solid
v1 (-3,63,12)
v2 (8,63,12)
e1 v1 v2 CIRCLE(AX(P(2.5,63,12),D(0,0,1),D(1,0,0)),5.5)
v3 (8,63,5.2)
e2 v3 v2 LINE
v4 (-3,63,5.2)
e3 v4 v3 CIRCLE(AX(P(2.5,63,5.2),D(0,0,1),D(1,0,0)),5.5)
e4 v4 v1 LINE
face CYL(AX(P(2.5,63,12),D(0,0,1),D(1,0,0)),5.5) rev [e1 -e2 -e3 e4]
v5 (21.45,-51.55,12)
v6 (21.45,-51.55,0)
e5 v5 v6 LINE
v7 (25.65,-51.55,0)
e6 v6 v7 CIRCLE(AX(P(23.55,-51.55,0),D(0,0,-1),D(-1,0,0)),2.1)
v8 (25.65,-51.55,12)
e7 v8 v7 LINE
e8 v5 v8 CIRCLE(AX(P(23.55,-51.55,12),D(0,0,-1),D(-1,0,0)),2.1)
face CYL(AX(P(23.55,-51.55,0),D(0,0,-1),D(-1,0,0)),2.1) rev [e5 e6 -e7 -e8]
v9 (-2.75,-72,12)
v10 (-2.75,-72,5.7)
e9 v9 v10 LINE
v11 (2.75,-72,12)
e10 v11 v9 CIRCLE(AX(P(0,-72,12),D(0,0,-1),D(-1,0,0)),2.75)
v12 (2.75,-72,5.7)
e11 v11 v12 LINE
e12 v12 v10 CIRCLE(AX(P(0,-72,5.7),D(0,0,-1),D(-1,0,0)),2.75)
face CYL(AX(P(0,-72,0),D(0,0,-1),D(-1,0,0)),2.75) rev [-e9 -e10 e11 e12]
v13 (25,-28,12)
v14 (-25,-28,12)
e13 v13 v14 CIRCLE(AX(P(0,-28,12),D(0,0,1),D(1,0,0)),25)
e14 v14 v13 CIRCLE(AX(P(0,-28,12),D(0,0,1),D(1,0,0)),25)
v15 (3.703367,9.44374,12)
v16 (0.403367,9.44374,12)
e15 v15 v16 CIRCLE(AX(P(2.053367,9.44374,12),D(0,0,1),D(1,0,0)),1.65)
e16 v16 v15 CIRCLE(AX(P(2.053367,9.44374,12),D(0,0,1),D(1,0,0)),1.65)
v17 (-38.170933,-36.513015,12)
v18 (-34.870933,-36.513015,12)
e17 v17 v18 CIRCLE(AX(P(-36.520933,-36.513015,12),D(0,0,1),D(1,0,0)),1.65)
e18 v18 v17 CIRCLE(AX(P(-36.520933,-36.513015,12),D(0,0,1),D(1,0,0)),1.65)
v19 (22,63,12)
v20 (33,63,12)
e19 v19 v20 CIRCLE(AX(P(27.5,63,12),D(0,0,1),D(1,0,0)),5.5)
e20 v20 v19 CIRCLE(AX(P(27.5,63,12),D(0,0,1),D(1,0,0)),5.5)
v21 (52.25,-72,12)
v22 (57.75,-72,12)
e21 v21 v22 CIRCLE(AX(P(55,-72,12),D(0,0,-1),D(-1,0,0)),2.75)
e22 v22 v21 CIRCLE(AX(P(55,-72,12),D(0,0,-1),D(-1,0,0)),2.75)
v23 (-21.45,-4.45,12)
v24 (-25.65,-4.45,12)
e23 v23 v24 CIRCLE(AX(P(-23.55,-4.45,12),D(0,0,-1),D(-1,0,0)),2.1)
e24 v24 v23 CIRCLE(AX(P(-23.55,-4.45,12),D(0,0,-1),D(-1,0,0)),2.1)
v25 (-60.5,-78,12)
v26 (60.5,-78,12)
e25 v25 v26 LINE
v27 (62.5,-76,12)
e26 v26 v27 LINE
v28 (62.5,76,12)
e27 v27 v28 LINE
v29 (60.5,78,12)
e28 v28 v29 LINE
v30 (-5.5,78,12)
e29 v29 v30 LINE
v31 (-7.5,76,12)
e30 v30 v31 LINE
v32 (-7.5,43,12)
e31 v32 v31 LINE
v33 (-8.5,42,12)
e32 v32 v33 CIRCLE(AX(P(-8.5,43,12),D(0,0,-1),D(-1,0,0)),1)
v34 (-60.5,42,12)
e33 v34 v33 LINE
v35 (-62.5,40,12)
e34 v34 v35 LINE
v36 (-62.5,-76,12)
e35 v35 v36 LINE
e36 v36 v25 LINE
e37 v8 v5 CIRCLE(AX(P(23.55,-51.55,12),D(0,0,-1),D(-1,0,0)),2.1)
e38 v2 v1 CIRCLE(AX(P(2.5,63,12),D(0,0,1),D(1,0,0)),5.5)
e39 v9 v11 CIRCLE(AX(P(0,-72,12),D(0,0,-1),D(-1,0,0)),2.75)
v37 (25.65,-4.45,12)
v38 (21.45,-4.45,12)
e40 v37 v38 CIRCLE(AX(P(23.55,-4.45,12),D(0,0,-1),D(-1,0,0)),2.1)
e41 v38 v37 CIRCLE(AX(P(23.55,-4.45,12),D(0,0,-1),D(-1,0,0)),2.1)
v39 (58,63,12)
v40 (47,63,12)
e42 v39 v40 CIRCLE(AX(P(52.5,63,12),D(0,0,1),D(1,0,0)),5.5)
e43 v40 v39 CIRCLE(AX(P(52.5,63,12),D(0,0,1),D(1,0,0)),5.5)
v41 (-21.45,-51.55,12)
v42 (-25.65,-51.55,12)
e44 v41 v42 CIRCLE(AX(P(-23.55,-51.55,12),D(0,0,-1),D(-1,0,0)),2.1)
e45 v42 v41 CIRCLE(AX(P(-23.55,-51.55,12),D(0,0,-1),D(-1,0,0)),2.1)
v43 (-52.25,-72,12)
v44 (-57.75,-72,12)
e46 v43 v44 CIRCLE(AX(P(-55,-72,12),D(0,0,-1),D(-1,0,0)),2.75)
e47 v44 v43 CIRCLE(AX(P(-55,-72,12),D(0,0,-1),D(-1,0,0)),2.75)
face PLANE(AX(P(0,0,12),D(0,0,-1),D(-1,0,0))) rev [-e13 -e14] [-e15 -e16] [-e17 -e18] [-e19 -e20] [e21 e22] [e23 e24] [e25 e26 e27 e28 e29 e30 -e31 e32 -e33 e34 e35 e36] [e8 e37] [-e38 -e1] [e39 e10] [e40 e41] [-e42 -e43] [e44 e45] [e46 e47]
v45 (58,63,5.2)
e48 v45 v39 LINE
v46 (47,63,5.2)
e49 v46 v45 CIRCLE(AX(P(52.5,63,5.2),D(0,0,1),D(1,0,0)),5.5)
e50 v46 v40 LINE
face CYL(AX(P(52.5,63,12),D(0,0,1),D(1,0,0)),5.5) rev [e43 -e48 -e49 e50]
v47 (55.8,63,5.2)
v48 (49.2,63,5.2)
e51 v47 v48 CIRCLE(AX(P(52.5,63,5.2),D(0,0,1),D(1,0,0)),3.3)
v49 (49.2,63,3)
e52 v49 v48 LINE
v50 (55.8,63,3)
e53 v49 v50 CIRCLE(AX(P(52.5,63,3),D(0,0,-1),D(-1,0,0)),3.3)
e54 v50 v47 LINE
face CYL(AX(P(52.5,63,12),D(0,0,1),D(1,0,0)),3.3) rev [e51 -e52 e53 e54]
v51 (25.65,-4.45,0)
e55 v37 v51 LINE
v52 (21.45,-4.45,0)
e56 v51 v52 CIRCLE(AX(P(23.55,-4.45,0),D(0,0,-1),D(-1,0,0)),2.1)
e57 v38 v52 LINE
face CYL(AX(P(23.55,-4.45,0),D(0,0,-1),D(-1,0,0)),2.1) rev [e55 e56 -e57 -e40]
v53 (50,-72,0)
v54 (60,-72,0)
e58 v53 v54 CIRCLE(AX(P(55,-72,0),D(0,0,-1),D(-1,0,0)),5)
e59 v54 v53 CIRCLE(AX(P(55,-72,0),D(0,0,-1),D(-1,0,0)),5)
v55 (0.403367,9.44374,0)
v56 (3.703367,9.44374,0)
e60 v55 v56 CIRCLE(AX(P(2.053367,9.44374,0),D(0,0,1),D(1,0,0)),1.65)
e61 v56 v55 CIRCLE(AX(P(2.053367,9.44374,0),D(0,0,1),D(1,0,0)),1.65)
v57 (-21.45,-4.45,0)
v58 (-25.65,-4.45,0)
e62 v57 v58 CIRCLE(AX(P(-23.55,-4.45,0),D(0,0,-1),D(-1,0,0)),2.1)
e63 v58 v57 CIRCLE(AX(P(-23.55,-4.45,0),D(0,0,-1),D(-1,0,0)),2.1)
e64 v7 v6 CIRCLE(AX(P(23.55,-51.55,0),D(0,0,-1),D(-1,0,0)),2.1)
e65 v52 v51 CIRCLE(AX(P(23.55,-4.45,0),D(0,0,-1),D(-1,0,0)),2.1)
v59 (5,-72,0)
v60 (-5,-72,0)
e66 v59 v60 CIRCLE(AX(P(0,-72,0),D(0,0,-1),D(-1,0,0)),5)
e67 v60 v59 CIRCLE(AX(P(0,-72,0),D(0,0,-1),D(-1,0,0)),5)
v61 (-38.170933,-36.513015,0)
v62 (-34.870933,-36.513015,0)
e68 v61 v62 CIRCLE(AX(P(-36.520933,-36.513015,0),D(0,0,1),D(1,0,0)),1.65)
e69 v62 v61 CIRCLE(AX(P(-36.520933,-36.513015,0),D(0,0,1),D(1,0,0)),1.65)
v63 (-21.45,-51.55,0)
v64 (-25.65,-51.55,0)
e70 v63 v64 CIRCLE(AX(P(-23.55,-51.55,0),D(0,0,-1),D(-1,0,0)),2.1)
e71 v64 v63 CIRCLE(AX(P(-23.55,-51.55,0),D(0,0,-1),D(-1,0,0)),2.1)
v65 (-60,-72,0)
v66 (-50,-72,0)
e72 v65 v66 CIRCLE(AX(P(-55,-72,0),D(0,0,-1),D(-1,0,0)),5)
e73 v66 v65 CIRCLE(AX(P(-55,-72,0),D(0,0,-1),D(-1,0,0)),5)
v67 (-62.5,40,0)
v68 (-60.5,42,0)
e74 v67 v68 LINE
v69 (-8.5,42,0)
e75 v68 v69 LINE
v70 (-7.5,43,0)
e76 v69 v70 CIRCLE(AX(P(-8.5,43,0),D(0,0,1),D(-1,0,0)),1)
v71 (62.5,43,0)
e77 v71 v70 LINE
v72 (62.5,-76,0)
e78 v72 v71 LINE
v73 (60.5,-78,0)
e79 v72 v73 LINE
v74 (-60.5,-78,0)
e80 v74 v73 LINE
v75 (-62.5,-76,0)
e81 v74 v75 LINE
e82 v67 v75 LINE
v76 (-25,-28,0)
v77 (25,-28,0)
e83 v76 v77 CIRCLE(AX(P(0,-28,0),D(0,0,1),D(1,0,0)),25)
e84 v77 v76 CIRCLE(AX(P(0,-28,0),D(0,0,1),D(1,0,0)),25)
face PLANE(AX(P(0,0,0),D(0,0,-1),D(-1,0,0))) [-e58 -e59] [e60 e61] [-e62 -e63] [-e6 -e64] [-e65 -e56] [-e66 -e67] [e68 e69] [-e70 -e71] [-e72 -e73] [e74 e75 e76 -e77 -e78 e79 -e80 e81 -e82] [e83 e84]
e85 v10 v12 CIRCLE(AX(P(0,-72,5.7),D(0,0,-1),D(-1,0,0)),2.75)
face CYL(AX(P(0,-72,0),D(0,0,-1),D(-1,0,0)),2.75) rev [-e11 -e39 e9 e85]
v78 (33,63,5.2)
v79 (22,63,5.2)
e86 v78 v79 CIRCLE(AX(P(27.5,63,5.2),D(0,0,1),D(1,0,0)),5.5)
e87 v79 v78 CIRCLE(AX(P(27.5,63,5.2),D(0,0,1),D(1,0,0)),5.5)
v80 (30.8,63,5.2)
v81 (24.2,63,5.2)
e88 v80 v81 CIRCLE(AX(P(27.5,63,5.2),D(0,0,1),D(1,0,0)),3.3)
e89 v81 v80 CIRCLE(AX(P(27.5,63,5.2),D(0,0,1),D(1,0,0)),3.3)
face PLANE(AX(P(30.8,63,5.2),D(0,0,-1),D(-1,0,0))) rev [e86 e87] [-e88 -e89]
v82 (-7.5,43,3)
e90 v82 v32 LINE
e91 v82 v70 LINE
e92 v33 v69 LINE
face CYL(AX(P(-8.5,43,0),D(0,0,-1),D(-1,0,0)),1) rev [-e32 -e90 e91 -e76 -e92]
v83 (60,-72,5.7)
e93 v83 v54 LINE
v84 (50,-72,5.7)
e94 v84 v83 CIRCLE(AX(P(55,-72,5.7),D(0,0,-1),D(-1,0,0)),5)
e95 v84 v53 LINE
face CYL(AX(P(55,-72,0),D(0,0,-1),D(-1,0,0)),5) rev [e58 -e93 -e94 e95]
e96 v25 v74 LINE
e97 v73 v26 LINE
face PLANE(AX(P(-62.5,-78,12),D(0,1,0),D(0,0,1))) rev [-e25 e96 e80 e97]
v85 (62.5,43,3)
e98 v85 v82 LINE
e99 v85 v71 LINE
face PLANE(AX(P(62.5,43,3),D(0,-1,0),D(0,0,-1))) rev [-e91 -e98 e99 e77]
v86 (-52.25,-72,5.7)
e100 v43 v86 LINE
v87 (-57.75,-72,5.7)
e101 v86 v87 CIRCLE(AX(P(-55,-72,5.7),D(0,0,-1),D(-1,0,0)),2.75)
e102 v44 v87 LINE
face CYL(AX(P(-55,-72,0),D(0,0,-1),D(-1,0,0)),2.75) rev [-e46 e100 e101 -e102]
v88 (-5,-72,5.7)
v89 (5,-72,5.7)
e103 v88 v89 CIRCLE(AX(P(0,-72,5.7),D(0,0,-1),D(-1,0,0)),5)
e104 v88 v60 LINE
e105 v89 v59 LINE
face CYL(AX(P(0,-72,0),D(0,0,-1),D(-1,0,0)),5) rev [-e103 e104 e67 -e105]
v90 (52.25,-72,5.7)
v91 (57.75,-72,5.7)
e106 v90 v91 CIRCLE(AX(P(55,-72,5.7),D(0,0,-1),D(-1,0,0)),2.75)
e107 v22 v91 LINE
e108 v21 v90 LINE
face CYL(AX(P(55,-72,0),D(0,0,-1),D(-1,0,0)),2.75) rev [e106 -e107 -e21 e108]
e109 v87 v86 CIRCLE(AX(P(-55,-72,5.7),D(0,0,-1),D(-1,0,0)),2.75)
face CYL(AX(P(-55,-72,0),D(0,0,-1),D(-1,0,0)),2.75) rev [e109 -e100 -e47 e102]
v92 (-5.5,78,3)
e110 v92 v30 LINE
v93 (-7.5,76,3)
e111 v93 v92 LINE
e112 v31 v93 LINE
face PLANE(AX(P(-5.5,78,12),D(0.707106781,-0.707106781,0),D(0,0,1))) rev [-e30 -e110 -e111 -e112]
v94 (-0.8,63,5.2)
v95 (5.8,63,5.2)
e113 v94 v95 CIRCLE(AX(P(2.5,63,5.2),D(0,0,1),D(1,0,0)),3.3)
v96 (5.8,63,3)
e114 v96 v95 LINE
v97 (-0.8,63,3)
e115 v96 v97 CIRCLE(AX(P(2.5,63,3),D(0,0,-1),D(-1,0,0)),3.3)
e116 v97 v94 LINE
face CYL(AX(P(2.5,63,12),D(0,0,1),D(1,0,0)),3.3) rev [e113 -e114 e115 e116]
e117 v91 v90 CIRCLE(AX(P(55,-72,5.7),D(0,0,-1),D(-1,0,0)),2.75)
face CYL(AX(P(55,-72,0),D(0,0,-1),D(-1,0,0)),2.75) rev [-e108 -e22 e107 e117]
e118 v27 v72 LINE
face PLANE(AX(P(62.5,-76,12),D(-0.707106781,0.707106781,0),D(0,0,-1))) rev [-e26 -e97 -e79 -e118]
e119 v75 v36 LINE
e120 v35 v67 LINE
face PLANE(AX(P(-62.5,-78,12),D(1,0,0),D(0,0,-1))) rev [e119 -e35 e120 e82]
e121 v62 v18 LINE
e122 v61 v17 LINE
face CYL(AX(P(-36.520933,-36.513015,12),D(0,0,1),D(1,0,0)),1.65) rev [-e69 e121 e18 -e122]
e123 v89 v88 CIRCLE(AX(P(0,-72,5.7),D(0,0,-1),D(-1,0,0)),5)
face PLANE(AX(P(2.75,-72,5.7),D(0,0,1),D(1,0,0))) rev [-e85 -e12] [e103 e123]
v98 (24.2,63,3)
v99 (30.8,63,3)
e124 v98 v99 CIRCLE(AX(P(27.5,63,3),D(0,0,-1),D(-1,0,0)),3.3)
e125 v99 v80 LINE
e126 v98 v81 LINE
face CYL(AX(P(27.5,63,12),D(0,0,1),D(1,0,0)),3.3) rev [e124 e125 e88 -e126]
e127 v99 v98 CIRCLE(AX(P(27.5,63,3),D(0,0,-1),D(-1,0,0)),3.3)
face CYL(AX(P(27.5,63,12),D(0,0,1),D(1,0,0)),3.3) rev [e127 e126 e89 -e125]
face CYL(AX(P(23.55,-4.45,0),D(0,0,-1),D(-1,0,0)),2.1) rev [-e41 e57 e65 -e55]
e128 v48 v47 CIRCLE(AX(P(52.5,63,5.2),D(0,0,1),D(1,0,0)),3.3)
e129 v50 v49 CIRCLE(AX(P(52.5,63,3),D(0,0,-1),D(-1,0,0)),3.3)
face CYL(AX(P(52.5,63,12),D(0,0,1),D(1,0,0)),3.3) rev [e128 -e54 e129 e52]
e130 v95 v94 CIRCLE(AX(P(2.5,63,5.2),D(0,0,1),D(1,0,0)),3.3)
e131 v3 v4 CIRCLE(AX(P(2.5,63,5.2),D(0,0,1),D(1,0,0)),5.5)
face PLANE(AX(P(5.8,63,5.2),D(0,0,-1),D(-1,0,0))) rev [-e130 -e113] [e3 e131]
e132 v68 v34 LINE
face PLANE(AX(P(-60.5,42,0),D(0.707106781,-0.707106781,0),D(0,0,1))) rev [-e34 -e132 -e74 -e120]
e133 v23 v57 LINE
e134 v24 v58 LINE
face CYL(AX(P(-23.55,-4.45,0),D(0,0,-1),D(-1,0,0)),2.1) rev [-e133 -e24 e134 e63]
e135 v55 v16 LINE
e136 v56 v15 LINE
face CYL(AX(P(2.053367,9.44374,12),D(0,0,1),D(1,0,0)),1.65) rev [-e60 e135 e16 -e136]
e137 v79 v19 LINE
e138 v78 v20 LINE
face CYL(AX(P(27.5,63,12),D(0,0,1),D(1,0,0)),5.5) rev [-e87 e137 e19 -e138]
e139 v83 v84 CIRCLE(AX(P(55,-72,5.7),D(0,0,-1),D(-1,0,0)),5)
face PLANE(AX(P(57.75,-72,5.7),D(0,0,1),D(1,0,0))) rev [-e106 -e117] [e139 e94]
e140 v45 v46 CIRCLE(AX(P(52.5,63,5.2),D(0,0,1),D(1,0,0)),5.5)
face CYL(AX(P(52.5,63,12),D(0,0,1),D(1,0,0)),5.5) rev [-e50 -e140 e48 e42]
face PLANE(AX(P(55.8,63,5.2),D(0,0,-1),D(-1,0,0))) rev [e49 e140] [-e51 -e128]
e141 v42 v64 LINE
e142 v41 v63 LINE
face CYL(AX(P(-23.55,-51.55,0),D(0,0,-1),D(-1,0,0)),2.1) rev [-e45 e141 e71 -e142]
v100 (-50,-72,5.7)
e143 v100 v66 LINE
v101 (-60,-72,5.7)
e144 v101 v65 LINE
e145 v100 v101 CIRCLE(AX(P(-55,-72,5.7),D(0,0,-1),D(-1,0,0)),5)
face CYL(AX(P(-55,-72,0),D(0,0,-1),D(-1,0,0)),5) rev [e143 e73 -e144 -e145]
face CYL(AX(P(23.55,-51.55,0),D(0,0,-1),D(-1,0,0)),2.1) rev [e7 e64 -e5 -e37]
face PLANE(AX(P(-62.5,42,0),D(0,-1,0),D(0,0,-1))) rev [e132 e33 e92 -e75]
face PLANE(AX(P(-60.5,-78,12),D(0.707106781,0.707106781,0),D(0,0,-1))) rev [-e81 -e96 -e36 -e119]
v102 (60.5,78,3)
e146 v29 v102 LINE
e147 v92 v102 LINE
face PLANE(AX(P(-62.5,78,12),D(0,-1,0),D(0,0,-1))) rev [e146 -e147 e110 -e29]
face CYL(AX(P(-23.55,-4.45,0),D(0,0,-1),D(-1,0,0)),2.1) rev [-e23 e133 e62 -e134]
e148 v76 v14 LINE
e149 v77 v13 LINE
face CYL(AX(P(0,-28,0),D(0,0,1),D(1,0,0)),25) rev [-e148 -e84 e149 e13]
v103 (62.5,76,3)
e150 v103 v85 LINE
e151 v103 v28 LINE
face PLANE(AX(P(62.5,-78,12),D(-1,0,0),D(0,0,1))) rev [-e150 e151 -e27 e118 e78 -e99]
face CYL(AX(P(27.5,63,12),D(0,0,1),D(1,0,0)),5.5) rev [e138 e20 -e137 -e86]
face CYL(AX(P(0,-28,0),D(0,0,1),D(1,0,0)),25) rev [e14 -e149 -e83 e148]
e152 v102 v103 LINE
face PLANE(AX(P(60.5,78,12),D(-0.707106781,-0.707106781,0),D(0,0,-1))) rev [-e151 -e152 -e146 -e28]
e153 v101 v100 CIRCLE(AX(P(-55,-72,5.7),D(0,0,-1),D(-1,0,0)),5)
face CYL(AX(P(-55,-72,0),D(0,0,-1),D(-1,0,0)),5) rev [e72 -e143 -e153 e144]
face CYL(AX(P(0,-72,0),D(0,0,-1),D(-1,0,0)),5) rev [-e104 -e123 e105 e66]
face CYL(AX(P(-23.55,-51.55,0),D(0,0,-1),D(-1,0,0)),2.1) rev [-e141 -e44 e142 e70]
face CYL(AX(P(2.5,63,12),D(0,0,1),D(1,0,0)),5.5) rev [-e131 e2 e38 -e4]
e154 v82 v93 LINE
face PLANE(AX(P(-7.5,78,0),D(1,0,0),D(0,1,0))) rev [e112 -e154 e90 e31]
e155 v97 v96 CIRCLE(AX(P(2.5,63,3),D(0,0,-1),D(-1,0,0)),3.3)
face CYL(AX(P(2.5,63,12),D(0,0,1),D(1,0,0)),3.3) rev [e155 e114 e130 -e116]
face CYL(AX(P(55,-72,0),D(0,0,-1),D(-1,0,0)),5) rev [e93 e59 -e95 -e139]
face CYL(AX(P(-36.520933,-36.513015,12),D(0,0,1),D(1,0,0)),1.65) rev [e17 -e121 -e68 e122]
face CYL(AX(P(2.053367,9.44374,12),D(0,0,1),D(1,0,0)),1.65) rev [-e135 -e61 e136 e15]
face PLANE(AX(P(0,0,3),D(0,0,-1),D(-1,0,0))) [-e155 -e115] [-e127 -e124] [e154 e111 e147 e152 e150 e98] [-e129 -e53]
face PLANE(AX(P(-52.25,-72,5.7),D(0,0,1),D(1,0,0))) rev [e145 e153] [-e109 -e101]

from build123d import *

# Parameters (mm, degrees)
SKETCH_1_W                = 125
SKETCH_1_H                = 156
EXTRUDE_1_DEPTH           = 12
SKETCH_2_W                = 55
SKETCH_2_H                = 36
CUT_EXTRUDE_1_DEPTH       = 101.669012114
SKETCH_3_W                = 70
SKETCH_3_H                = 35
CUT_EXTRUDE_2_DEPTH       = 3
HOLE_WIZARD_1_D           = 5.5
HOLE_WIZARD_1_CBORE_D     = 10
HOLE_WIZARD_1_CBORE_DEPTH = 5.7
HOLE_WIZARD_2_D           = 6.6
HOLE_WIZARD_2_CBORE_D     = 11
HOLE_WIZARD_2_CBORE_DEPTH = 6.8
CHAMFER_1_SIZE            = 2
FILLET_1_R                = 1
SKETCH_10_R               = 25
CUT_EXTRUDE_3_DEPTH       = 101.669012114
HOLE_WIZARD_M5_1_D        = 4.2
HOLE_WIZARD_M4_1_D        = 3.3


with BuildPart() as part:
    # 草图1 → 凸台-拉伸1 (new body)
    with BuildSketch(Plane.XY):
        Rectangle(SKETCH_1_W, SKETCH_1_H)
    extrude(amount=EXTRUDE_1_DEPTH)

    # 草图2 → 切除-拉伸1 (cut, through all)
    with BuildSketch(Plane.XY.offset(12)):
        with Locations((-35, 60)):
            Rectangle(SKETCH_2_W, SKETCH_2_H)
    extrude(amount=-CUT_EXTRUDE_1_DEPTH, mode=Mode.SUBTRACT)

    # 草图3 → 切除-拉伸2 (cut)
    with BuildSketch(Plane(origin=(0, 0, 0), x_dir=(-1, 0, 0), z_dir=(0, 0, -1))):
        with Locations((-27.5, 60.5)):
            Rectangle(SKETCH_3_W, SKETCH_3_H)
    extrude(amount=-CUT_EXTRUDE_2_DEPTH, mode=Mode.SUBTRACT)

    # 打孔尺寸(%根据)内六角圆柱头螺钉的类型1 (through all)
    with Locations(Plane(origin=(0, 0, 0), x_dir=(-1, 0, 0), z_dir=(0, 0, -1))):
        with Locations((-55, -72), (0, -72), (55, -72)):
            CounterBoreHole(HOLE_WIZARD_1_D / 2, HOLE_WIZARD_1_CBORE_D / 2, HOLE_WIZARD_1_CBORE_DEPTH)

    # 打孔尺寸(%根据)内六角圆柱头螺钉的类型2 (through all)
    with Locations(Plane(origin=(0, 0, 12), x_dir=(-1, 0, 0), z_dir=(0, 0, 1))):
        with Locations((-52.5, -63), (-27.5, -63), (-2.5, -63)):
            CounterBoreHole(HOLE_WIZARD_2_D / 2, HOLE_WIZARD_2_CBORE_D / 2, HOLE_WIZARD_2_CBORE_DEPTH)

    # 倒角1
    chamfer_1_edges = [part.edges().sort_by_distance(p)[0] for p in [
        (-62.5, 42, 6),
        (-7.5, 78, 7.5),
        (62.5, -78, 6),
        (-62.5, -78, 6),
        (62.5, 78, 7.5),
    ]]
    chamfer(chamfer_1_edges, length=CHAMFER_1_SIZE)

    # 圆角1
    fillet_1_edges = [part.edges().sort_by_distance(p)[0] for p in [
        (-7.5, 42, 6),
    ]]
    fillet(fillet_1_edges, radius=FILLET_1_R)

    # 草图10 → 切除-拉伸3 (cut, through all)
    with BuildSketch(Plane.XY.offset(12)):
        with Locations((0, -28)):
            Circle(SKETCH_10_R)
    extrude(amount=-CUT_EXTRUDE_3_DEPTH, mode=Mode.SUBTRACT)

    # M5 螺纹孔1 (through all)
    with Locations(Plane(origin=(0, 0, 0), x_dir=(-1, 0, 0), z_dir=(0, 0, -1))):
        with Locations((-23.55, -4.45), (23.55, -4.45), (23.55, -51.55), (-23.55, -51.55)):
            Hole(HOLE_WIZARD_M5_1_D / 2)

    # M4 螺纹孔1 (through all)
    with Locations(Plane.XY.offset(12)):
        with Locations((2.053366632, 9.443740271), (-36.520933317, -36.513015309)):
            Hole(HOLE_WIZARD_M4_1_D / 2)


solid = part.part
